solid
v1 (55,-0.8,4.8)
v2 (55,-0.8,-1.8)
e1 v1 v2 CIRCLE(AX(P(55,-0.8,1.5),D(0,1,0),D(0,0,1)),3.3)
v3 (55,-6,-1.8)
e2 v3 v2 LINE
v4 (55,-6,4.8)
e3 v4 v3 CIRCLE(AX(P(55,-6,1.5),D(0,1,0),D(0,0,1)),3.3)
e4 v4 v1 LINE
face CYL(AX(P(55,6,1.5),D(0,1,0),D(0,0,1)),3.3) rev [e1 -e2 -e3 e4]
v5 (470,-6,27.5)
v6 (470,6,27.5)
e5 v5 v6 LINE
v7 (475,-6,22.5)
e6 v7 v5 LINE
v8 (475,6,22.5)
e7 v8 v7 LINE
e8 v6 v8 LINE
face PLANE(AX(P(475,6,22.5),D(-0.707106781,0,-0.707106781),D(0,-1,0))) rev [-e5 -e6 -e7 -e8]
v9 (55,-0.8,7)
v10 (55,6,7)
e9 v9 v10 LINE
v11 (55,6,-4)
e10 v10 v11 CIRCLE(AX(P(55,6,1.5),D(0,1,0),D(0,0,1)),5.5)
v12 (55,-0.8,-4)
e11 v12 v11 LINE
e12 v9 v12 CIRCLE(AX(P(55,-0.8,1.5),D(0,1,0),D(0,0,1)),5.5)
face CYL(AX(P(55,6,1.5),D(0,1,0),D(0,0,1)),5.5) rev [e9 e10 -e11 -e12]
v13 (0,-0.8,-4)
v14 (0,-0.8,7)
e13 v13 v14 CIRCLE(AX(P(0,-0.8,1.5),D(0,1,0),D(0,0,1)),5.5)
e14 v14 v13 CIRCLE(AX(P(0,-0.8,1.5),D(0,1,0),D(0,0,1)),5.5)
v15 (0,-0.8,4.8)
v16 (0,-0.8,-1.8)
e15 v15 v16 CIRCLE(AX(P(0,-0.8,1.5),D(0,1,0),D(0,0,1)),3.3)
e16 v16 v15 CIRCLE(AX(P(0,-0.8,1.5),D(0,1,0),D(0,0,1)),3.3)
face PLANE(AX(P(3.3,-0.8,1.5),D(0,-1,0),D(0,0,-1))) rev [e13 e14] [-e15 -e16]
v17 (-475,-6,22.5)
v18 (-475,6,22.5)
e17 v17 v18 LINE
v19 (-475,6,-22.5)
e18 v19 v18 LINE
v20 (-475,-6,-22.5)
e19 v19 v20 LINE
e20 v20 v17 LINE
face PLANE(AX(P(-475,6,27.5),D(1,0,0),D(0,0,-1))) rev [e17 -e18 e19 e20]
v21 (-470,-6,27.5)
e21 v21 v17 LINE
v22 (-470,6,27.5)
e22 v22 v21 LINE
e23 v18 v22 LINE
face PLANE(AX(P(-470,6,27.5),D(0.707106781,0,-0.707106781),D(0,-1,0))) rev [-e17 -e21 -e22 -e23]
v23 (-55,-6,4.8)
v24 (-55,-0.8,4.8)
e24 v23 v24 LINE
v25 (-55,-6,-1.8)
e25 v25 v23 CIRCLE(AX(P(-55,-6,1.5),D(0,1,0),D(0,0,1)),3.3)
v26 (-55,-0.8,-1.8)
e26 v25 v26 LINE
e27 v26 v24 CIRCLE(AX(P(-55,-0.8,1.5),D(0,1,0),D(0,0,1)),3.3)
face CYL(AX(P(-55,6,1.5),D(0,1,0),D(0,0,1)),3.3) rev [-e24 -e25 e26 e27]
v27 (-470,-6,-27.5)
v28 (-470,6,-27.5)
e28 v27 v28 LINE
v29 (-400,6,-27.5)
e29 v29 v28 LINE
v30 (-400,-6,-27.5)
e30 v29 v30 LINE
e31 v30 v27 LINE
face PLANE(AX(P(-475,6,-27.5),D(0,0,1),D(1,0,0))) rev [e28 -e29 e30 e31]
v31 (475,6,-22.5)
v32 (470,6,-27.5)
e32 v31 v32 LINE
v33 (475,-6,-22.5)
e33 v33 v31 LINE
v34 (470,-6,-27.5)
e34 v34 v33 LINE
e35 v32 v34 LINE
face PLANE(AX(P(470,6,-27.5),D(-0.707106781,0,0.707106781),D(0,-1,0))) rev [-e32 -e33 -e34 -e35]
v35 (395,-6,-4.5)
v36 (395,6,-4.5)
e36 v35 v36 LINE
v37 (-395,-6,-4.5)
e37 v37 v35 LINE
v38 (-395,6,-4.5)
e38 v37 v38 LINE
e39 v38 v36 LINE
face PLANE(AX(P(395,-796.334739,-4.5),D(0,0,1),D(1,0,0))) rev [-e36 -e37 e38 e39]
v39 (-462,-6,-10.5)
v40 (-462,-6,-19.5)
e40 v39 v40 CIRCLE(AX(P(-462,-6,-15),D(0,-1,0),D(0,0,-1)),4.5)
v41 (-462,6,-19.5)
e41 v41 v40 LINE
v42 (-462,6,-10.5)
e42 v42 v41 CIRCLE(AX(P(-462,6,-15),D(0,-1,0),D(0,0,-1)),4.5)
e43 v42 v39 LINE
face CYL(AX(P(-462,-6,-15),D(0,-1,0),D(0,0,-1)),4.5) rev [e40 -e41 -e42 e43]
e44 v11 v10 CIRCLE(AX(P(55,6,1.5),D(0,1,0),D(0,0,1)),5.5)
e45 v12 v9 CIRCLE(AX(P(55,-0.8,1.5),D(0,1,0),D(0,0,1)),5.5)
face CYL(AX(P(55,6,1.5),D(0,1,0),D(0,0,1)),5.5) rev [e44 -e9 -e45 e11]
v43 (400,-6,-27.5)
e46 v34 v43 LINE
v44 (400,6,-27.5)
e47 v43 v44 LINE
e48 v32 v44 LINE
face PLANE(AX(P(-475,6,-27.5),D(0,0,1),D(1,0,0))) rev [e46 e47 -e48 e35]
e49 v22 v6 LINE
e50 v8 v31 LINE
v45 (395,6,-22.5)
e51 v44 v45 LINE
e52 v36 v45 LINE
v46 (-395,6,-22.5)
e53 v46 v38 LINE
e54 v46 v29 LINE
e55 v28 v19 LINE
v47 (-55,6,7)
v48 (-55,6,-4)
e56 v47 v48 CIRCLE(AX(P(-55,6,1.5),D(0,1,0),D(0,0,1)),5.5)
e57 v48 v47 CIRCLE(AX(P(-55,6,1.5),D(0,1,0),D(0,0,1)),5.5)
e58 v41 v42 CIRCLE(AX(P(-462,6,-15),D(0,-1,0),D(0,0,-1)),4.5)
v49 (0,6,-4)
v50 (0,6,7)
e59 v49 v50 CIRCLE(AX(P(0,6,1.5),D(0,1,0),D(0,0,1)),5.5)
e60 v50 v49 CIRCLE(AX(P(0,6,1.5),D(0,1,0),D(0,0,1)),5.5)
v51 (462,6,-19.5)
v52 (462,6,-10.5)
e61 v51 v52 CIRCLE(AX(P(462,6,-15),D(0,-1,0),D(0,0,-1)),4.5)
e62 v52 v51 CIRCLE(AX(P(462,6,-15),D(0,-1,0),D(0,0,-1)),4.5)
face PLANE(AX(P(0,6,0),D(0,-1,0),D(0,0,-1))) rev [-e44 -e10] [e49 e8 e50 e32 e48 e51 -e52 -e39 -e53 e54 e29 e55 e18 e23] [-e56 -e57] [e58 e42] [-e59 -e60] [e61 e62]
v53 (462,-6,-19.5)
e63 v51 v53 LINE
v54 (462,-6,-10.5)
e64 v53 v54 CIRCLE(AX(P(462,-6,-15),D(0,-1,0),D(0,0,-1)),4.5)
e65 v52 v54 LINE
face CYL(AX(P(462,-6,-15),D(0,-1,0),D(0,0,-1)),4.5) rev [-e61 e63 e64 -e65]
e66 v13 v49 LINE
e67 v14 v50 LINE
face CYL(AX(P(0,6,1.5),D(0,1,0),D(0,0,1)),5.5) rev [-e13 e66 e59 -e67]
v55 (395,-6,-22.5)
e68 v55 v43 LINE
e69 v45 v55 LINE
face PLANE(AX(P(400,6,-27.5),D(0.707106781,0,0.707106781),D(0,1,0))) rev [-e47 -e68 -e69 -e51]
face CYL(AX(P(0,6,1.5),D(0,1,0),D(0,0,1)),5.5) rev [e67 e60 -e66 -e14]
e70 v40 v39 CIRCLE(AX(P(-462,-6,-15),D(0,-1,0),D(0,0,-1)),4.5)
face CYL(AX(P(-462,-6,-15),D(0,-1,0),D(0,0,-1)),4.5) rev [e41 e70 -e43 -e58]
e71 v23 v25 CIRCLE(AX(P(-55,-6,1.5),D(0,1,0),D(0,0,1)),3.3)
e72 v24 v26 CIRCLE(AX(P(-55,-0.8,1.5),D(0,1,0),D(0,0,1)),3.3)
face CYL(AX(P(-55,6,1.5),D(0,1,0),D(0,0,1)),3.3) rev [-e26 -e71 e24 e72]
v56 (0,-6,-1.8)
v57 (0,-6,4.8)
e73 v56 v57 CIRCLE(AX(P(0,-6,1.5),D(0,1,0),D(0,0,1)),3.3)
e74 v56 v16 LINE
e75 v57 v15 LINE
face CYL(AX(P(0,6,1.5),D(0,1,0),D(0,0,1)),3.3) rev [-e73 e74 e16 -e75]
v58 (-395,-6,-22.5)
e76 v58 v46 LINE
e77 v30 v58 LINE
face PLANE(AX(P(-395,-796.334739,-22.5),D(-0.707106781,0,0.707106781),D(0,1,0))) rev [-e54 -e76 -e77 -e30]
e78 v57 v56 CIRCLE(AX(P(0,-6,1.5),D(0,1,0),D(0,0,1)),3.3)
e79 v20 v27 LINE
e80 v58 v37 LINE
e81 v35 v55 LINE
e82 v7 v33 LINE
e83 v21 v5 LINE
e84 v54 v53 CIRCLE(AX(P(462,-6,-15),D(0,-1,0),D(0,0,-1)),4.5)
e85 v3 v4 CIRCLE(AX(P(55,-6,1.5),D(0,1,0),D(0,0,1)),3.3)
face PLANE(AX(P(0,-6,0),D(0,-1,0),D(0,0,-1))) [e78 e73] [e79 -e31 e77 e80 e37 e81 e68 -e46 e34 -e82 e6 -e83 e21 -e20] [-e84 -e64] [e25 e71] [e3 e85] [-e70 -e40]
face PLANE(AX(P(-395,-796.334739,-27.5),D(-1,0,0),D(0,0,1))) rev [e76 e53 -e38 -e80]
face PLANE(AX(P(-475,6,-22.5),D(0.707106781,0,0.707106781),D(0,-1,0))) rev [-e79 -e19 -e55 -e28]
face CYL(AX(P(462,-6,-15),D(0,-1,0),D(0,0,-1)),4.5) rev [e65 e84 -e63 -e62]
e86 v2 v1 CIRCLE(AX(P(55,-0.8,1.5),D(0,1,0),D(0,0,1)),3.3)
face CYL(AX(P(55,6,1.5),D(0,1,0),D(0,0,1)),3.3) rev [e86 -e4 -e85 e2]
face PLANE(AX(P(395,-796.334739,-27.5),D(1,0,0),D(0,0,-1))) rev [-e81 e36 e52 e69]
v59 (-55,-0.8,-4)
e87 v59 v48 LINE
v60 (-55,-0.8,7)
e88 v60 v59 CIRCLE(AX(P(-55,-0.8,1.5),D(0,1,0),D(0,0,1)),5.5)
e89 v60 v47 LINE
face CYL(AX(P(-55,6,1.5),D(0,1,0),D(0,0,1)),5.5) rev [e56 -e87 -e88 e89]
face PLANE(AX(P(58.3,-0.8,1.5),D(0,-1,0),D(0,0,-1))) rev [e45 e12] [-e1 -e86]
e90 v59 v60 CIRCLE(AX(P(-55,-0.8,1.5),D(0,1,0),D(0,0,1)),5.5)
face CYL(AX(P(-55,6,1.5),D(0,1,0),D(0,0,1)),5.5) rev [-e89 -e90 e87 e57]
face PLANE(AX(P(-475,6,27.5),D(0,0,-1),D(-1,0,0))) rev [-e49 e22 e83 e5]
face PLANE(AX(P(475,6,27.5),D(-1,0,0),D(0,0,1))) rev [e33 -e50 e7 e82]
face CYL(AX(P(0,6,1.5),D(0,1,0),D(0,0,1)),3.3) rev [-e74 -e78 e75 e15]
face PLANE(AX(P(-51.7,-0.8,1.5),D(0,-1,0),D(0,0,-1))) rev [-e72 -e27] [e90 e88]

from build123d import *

# Parameters (mm, degrees)
SKETCH_1_W                = 950
SKETCH_1_H                = 55
EXTRUDE_1_DEPTH           = 6
SKETCH_2_W                = 790
SKETCH_2_H                = 23
CUT_EXTRUDE_1_DEPTH       = 12
CHAMFER_1_SIZE            = 5
HOLE_WIZARD_M8_1_D        = 9
HOLE_WIZARD_1_D           = 6.6
HOLE_WIZARD_1_CBORE_D     = 11
HOLE_WIZARD_1_CBORE_DEPTH = 6.8


with BuildPart() as part:
    # 草图1 → 凸台-拉伸1 (new, symmetric)
    with BuildSketch(Plane(origin=(0, 0, 0), x_dir=(1, 0, 0), z_dir=(0, 1, 0))):
        Rectangle(SKETCH_1_W, SKETCH_1_H)
    extrude(amount=EXTRUDE_1_DEPTH, both=True)

    # 草图2 → 切除-拉伸1 (cut)
    with BuildSketch(Plane(origin=(0, 6, 0), x_dir=(1, 0, 0), z_dir=(0, 1, 0))):
        with Locations((0, 16)):
            Rectangle(SKETCH_2_W, SKETCH_2_H)
    extrude(amount=-CUT_EXTRUDE_1_DEPTH, mode=Mode.SUBTRACT)

    # 倒角1
    chamfer_1_edges = [part.edges().sort_by_distance(p)[0] for p in [
        (-395, 0, -27.5),
        (395, 0, -27.5),
        (475, 0, 27.5),
        (-475, 0, 27.5),
        (-475, 0, -27.5),
        (475, 0, -27.5),
    ]]
    chamfer(chamfer_1_edges, length=CHAMFER_1_SIZE)

    # M8 间隙孔1 (through all)
    with Locations(Plane(origin=(0, -6, 0), x_dir=(-1, 0, 0), z_dir=(0, -1, 0))):
        with Locations((462, 15), (-462, 15)):
            Hole(HOLE_WIZARD_M8_1_D / 2)

    # 打孔尺寸(%根据)内六角圆柱头螺钉的类型1 (through all)
    with Locations(Plane(origin=(0, 6, 0), x_dir=(1, 0, 0), z_dir=(0, 1, 0))):
        with Locations((55, -1.5), (0, -1.5), (-55, -1.5)):
            CounterBoreHole(HOLE_WIZARD_1_D / 2, HOLE_WIZARD_1_CBORE_D / 2, HOLE_WIZARD_1_CBORE_DEPTH)


solid = part.part
